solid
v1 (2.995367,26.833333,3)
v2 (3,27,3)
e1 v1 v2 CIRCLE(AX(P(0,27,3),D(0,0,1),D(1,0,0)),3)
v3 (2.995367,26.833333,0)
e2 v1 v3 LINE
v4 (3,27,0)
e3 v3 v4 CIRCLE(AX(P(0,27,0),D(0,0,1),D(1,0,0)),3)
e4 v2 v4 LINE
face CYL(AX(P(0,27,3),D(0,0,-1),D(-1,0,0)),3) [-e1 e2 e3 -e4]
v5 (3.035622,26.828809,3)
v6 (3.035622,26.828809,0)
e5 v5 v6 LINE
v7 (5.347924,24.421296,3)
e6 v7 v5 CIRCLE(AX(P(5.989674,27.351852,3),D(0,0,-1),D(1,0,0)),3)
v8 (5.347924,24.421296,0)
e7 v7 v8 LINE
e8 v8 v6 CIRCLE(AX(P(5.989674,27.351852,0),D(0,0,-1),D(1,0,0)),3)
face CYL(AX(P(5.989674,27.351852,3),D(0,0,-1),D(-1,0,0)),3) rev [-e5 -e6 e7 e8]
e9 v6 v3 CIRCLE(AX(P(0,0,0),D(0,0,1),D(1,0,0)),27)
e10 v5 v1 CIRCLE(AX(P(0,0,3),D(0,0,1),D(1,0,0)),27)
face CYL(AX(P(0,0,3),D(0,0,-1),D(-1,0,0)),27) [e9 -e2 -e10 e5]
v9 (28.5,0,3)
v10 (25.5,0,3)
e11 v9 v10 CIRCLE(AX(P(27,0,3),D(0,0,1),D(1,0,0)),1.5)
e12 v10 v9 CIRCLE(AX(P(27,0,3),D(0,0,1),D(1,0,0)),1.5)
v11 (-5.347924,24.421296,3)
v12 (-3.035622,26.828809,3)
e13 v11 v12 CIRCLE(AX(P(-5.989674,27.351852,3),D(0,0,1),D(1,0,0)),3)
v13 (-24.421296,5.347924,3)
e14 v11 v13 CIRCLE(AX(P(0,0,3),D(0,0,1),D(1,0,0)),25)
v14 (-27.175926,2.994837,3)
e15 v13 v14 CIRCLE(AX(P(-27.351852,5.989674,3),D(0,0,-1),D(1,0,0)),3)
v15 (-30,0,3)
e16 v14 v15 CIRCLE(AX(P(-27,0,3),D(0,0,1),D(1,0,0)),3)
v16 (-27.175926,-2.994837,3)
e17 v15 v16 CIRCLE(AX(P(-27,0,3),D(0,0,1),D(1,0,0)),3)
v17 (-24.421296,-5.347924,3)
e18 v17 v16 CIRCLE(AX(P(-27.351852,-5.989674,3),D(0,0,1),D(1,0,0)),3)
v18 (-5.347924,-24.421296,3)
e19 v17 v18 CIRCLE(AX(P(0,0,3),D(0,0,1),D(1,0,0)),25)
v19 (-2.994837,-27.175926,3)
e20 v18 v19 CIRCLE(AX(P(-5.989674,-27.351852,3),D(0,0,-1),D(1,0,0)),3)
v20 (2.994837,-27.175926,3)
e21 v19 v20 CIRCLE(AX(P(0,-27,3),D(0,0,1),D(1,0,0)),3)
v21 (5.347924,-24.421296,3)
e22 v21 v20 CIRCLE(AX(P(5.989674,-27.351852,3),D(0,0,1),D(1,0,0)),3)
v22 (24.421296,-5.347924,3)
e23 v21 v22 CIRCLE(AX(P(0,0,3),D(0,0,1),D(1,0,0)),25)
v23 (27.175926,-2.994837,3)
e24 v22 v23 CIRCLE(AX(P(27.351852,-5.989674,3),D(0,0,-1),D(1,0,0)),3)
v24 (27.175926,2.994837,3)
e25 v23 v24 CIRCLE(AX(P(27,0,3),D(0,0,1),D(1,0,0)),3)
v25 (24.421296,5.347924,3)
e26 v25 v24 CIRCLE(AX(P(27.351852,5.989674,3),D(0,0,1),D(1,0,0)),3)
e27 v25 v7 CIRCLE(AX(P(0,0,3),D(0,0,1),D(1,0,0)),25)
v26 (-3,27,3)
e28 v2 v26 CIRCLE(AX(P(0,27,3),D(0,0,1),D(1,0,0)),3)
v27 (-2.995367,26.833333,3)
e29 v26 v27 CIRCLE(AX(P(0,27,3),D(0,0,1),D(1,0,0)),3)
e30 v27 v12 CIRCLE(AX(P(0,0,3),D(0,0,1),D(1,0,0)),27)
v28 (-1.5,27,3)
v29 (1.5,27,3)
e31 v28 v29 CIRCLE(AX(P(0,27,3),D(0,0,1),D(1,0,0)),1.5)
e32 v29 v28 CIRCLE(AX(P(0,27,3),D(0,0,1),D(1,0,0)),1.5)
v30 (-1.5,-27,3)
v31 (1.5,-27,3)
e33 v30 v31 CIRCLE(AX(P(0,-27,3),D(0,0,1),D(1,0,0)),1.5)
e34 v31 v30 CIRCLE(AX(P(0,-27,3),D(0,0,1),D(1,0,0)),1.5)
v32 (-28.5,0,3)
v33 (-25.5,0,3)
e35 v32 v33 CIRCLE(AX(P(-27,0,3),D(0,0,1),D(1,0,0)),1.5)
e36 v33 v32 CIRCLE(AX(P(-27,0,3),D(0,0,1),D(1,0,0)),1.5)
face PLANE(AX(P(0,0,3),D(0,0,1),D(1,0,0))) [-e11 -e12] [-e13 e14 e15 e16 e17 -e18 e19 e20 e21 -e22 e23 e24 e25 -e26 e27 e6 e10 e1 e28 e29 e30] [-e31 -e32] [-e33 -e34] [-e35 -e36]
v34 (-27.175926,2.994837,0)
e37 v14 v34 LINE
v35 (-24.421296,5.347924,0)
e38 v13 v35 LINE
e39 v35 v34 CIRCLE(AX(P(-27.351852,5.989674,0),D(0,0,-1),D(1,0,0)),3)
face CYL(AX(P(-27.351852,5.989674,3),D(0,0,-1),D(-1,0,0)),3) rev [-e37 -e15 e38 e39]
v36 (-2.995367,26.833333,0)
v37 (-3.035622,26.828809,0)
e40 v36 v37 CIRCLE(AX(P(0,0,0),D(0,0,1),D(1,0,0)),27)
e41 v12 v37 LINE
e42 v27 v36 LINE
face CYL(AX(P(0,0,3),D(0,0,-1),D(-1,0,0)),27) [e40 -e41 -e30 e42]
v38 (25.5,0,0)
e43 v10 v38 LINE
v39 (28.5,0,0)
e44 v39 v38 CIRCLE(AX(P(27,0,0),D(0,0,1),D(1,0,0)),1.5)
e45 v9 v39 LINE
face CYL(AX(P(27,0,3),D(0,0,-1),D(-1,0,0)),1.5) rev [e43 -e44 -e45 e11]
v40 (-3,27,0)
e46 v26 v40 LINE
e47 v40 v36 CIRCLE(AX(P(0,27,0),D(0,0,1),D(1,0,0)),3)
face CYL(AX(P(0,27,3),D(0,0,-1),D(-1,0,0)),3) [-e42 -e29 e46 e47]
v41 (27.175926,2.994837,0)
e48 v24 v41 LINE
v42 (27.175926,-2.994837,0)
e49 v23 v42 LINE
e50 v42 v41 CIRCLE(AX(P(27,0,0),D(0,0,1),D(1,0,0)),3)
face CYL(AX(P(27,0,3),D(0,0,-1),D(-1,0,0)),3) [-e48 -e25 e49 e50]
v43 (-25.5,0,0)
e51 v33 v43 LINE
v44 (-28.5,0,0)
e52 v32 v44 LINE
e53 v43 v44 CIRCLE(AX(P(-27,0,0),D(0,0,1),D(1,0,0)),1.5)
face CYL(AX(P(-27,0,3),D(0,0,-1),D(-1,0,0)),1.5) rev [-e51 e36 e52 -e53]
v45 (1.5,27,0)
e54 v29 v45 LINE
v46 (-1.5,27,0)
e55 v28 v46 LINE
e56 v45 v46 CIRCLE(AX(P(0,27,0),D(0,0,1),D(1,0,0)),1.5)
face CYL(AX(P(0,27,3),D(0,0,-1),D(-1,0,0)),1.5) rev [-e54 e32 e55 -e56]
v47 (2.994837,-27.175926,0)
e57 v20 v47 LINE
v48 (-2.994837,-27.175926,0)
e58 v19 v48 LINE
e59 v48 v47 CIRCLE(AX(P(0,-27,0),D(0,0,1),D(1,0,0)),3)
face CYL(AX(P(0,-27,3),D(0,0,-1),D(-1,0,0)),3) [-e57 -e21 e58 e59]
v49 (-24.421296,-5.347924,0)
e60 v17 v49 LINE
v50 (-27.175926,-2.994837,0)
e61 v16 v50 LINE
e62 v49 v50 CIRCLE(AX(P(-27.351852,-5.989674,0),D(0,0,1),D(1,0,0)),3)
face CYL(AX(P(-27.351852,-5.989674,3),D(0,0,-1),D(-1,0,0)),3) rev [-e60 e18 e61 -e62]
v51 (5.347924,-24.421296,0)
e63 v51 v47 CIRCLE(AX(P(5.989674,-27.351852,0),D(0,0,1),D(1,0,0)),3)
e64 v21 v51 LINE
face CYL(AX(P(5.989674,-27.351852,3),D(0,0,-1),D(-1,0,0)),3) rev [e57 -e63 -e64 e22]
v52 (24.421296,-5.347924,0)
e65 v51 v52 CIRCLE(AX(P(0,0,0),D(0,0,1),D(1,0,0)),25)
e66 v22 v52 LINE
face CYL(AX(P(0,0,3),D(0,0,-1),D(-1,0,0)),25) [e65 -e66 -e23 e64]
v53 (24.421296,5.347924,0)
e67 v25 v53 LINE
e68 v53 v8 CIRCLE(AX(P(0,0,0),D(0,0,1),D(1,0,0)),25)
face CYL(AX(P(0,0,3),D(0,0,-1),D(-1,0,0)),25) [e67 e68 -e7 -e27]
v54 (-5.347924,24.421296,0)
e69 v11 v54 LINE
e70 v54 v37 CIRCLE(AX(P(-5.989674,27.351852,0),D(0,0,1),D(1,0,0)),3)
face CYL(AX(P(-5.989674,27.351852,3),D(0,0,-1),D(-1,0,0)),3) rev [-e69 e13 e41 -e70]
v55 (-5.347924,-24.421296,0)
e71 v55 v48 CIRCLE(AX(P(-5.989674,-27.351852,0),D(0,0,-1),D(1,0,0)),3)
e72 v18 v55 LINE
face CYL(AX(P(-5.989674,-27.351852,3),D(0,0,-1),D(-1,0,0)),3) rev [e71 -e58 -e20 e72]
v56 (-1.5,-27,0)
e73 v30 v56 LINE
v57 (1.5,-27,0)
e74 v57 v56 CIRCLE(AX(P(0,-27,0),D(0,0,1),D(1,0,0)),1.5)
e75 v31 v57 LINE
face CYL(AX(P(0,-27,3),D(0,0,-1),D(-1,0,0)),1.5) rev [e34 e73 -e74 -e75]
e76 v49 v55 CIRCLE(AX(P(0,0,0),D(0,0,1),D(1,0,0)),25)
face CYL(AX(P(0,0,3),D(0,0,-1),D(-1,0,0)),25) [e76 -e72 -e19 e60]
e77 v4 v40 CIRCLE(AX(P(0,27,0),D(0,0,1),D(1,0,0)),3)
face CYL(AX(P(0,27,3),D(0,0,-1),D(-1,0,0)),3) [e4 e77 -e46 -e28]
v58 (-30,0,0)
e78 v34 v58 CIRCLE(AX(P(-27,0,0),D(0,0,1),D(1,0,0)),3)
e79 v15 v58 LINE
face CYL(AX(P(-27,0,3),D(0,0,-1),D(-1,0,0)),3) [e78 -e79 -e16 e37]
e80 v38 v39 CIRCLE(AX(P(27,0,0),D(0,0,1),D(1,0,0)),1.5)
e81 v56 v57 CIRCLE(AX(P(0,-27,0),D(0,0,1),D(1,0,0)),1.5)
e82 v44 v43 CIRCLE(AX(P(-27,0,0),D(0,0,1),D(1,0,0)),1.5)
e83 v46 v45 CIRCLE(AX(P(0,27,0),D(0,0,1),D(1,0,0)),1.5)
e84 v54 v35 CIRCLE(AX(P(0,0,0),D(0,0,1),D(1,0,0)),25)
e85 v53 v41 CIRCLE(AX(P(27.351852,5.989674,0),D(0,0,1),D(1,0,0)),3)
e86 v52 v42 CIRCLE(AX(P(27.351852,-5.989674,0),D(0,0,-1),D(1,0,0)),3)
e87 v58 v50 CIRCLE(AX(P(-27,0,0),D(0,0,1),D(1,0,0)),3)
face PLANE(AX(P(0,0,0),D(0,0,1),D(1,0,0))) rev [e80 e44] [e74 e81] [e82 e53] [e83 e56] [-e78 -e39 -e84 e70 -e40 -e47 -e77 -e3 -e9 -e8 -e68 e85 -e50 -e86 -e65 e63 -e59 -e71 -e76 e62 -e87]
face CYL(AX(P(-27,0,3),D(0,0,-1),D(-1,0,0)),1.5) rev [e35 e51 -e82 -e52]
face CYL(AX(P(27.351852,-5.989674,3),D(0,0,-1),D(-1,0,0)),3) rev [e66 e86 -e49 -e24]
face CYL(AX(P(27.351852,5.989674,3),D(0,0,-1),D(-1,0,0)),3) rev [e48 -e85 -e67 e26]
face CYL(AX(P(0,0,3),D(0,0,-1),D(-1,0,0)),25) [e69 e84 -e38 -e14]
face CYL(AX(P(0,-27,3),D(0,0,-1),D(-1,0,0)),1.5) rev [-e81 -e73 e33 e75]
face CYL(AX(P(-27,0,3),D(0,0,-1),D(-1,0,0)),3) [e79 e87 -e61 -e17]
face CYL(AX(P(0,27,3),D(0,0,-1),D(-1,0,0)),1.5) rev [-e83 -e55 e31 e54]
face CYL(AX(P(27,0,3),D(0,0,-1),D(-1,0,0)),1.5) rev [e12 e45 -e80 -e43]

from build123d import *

# Parameters (mm, degrees)
SKETCH_1_R      = 1.5
EXTRUDE_1_DEPTH = 3


with BuildPart() as part:
    # 草图1 → 凸台-拉伸1 (new body)
    with BuildSketch(Plane.XY):
        with BuildLine():
            ThreePointArc((-3.035621948, 26.828809131), (-3.826001677, 25.273746937), (-5.347923635, 24.421296296))
            ThreePointArc((-5.347923635, 24.421296296), (-17.67766953, 17.67766953), (-24.421296296, 5.347923635))
            ThreePointArc((-24.421296296, 5.347923635), (-25.403311193, 3.708624428), (-27.175925926, 2.994837236))
            ThreePointArc((-27.175925926, 2.994837236), (-30, 0), (-27.175925926, -2.994837236))
            ThreePointArc((-27.175925926, -2.994837236), (-25.403311193, -3.708624428), (-24.421296296, -5.347923635))
            ThreePointArc((-24.421296296, -5.347923635), (-17.67766953, -17.67766953), (-5.347923635, -24.421296296))
            ThreePointArc((-5.347923635, -24.421296296), (-3.708624428, -25.403311193), (-2.994837236, -27.175925926))
            ThreePointArc((-2.994837236, -27.175925926), (0, -30), (2.994837236, -27.175925926))
            ThreePointArc((2.994837236, -27.175925926), (3.708624428, -25.403311193), (5.347923635, -24.421296296))
            ThreePointArc((5.347923635, -24.421296296), (17.67766953, -17.67766953), (24.421296296, -5.347923635))
            ThreePointArc((24.421296296, -5.347923635), (25.403311193, -3.708624428), (27.175925926, -2.994837236))
            ThreePointArc((27.175925926, -2.994837236), (30, 0), (27.175925926, 2.994837236))
            ThreePointArc((27.175925926, 2.994837236), (25.403311193, 3.708624428), (24.421296296, 5.347923635))
            ThreePointArc((24.421296296, 5.347923635), (17.67766953, 17.67766953), (5.347923635, 24.421296296))
            ThreePointArc((5.347923635, 24.421296296), (3.826001677, 25.273746937), (3.035621948, 26.828809131))
            ThreePointArc((3.035621948, 26.828809131), (3.015495219, 26.831078782), (2.995366793, 26.833333333))
            ThreePointArc((2.995366793, 26.833333333), (2.999996416, 27.004637195), (2.994837236, 27.175925926))
            ThreePointArc((2.994837236, 27.175925926), (0, 30), (-2.994837236, 27.175925926))
            ThreePointArc((-2.994837236, 27.175925926), (-2.999996416, 27.004637195), (-2.995366793, 26.833333333))
            ThreePointArc((-2.995366793, 26.833333333), (-3.015495219, 26.831078782), (-3.035621948, 26.828809131))
        make_face()
        with Locations((-27, 0)):
            Circle(SKETCH_1_R, mode=Mode.SUBTRACT)
        with Locations((0, -27)):
            Circle(SKETCH_1_R, mode=Mode.SUBTRACT)
        with Locations((27, 0)):
            Circle(SKETCH_1_R, mode=Mode.SUBTRACT)
        with Locations((0, 27)):
            Circle(SKETCH_1_R, mode=Mode.SUBTRACT)
    extrude(amount=EXTRUDE_1_DEPTH)


solid = part.part
